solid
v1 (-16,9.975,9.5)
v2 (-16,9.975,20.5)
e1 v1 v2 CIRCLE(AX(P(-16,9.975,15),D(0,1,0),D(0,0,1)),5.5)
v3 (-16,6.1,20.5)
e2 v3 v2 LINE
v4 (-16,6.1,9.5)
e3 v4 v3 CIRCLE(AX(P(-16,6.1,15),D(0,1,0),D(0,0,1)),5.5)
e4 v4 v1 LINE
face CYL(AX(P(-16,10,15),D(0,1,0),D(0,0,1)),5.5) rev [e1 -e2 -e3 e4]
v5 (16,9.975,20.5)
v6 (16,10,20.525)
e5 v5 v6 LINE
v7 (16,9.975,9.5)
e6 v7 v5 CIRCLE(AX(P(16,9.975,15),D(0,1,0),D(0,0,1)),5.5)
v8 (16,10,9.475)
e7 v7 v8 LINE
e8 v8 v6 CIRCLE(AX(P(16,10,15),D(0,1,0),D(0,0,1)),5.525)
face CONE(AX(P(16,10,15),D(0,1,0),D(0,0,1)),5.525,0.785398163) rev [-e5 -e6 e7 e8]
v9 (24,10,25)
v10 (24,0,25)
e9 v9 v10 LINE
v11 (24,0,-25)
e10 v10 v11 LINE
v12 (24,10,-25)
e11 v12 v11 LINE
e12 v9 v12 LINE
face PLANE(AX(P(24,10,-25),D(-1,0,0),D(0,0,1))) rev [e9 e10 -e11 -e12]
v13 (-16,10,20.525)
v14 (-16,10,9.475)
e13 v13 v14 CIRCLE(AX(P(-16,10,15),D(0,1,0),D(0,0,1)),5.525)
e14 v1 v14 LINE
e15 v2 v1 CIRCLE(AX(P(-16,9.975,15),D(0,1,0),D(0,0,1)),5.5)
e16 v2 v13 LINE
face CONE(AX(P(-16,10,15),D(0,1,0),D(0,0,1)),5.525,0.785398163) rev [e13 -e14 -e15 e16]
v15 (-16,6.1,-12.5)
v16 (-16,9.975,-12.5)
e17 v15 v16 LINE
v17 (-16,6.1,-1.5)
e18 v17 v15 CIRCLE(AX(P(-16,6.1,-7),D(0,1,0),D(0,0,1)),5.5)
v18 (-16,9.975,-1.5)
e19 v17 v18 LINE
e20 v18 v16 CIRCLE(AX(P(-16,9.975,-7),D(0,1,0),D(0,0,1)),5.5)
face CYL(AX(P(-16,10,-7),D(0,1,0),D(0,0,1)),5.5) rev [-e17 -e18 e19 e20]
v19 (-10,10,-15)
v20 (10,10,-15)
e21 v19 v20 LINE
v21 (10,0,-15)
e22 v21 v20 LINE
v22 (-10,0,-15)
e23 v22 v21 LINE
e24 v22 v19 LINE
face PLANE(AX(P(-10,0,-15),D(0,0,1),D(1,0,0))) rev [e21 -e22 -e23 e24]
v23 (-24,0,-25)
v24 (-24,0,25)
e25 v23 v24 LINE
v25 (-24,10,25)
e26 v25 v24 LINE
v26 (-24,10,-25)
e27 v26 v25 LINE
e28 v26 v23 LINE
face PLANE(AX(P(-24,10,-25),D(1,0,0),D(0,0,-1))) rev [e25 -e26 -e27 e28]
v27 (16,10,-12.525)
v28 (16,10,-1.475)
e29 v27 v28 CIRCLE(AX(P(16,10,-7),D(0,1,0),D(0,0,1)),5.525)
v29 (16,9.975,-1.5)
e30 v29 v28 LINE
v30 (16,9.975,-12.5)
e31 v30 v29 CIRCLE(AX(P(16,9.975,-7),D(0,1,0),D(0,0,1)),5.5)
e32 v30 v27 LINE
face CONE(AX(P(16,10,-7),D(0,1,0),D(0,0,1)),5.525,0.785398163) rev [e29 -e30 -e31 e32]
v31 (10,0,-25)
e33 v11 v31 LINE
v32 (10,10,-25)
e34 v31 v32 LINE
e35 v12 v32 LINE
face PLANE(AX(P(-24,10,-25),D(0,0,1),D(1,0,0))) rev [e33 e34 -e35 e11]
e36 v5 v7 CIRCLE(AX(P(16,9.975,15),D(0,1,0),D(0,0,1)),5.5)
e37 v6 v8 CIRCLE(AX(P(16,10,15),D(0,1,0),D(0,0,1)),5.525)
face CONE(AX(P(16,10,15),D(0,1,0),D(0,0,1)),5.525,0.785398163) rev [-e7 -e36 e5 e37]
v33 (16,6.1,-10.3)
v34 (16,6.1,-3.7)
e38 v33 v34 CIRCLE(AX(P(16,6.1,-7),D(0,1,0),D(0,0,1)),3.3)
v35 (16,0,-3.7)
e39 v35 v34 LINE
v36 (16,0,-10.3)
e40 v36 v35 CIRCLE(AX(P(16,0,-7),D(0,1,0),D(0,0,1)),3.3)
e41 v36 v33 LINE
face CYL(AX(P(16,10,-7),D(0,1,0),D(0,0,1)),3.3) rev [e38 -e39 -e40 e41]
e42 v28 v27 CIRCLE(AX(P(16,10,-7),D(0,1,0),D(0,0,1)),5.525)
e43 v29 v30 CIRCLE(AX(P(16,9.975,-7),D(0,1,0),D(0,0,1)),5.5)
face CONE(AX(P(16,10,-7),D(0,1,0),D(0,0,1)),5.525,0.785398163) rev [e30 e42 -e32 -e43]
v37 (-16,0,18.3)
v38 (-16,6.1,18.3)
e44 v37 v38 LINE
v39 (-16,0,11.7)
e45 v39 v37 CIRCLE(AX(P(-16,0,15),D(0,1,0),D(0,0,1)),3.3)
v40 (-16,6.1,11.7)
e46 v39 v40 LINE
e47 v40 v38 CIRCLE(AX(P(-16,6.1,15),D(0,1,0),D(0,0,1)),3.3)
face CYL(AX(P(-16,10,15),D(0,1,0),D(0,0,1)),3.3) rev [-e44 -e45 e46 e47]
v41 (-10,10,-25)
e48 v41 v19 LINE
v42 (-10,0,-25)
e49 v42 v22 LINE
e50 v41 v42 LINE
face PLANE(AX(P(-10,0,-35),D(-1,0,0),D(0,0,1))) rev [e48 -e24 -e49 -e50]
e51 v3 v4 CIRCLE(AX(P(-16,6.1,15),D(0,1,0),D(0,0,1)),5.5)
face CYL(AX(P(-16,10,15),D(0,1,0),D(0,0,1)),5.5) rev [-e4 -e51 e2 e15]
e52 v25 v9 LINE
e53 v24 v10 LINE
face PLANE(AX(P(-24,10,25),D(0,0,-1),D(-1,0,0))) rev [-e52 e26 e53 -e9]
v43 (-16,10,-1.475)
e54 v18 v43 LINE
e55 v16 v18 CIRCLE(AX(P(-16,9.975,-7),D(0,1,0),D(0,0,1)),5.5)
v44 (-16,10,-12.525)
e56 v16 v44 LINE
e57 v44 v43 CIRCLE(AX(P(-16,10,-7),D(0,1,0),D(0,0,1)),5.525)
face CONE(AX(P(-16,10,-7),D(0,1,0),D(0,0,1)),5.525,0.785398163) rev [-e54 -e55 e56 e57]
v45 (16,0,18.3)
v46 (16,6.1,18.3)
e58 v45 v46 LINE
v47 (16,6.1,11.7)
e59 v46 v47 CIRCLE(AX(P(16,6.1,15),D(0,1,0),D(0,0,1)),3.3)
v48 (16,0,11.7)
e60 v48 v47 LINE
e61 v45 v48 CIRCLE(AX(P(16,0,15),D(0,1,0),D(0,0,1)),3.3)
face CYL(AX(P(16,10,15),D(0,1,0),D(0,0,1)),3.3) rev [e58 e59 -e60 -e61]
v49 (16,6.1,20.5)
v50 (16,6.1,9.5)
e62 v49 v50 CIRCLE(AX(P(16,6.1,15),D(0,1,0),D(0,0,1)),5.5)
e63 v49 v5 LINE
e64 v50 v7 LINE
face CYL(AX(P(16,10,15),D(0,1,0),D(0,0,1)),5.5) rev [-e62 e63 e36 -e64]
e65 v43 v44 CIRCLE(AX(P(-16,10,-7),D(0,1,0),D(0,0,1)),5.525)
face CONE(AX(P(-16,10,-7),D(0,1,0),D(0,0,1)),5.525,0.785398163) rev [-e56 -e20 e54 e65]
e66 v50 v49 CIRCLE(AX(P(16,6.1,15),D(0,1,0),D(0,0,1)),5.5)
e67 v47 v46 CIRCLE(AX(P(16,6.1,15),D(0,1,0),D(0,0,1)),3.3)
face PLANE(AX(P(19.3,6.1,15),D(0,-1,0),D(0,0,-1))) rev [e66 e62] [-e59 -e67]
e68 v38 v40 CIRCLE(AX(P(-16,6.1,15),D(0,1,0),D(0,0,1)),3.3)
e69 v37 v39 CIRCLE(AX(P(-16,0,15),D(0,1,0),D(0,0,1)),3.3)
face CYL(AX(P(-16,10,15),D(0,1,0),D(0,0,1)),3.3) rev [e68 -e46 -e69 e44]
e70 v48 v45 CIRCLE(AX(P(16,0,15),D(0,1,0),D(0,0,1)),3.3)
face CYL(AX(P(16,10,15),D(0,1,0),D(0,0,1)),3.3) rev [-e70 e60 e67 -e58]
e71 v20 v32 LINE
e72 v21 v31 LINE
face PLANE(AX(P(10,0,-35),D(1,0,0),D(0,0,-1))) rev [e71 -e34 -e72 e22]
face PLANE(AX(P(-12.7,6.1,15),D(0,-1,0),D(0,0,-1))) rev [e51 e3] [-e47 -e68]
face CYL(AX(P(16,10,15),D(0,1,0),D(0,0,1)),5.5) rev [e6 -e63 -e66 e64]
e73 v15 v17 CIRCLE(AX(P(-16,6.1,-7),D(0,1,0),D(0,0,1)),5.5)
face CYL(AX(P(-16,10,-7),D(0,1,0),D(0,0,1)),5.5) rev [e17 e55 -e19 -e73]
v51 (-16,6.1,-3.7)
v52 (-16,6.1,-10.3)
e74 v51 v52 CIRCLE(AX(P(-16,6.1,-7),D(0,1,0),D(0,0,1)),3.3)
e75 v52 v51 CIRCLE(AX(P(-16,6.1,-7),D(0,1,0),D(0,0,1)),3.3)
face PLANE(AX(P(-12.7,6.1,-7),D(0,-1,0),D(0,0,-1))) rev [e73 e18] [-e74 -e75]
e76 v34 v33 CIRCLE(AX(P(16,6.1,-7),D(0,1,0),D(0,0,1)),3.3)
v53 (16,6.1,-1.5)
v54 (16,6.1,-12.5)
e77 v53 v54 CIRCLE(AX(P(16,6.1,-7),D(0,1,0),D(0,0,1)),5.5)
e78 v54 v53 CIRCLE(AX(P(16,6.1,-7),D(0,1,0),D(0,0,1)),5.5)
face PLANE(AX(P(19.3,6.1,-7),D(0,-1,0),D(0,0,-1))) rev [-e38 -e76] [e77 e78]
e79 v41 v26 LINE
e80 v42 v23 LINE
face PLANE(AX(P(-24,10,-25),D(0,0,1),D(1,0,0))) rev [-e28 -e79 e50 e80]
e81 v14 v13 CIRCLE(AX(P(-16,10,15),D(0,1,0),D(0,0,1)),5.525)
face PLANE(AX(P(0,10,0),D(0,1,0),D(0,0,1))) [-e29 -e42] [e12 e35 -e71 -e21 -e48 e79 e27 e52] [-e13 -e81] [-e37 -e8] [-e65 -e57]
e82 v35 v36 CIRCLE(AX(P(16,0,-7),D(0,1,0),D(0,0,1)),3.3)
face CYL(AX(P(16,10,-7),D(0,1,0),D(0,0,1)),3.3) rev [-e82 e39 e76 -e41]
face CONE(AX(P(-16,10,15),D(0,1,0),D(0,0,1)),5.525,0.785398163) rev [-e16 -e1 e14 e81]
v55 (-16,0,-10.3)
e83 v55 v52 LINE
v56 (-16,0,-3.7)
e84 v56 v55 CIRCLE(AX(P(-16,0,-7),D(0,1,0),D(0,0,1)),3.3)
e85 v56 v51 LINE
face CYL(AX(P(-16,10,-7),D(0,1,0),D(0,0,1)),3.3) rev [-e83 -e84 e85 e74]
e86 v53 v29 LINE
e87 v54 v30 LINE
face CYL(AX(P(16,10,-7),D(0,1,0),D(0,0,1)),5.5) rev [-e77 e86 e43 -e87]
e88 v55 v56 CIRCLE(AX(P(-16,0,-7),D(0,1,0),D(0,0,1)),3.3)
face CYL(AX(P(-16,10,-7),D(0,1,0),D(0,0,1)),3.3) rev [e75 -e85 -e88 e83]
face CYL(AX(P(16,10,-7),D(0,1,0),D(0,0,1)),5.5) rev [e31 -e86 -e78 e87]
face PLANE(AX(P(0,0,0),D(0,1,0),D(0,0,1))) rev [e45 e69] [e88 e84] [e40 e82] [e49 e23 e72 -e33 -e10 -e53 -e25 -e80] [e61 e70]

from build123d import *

# Parameters (mm, degrees)
SKETCH1_W                                  = 48
SKETCH1_H                                  = 50
BOSS_EXTRUDE1_DEPTH                        = 10
SKETCH2_W                                  = 20
SKETCH2_H                                  = 20
CUT_EXTRUDE1_DEPTH                         = 10
CBORE_FOR_M6_CHEESE_HEAD_SCREW1_AT_2_COUNT = 2
CBORE_FOR_M6_CHEESE_HEAD_SCREW1_AT_2_PITCH = 22
CBORE_FOR_M6_CHEESE_HEAD_SCREW1_AT_3_COUNT = 2
CBORE_FOR_M6_CHEESE_HEAD_SCREW1_AT_3_PITCH = 38.832975678
CBORE_FOR_M6_CHEESE_HEAD_SCREW1_AT_4_COUNT = 2
CBORE_FOR_M6_CHEESE_HEAD_SCREW1_AT_4_PITCH = 32


with BuildPart() as part:
    # Sketch1 → Boss-Extrude1 (new body)
    with BuildSketch(Plane(origin=(0, 0, 0), x_dir=(1, 0, 0), z_dir=(0, 1, 0))):
        Rectangle(SKETCH1_W, SKETCH1_H)
    extrude(amount=BOSS_EXTRUDE1_DEPTH)

    # Sketch2 → Cut-Extrude1 (cut)
    with BuildSketch(Plane(origin=(0, 10, 0), x_dir=(1, 0, 0), z_dir=(0, 1, 0))):
        with Locations((0, 25)):
            Rectangle(SKETCH2_W, SKETCH2_H)
    extrude(amount=-CUT_EXTRUDE1_DEPTH, mode=Mode.SUBTRACT)

    # Sketch4 → CBORE for M6 Cheese Head Screw1 (revolve, cut)
    with BuildSketch(Plane(origin=(-16, 10, -7), x_dir=(0, 0, 1), z_dir=(1, 0, 0))):
        Polygon((0, 0), (0, 11.982840043), (3.3, 10), (3.3, 3.9), (5.5, 3.9), (5.5, 0.025), (5.525, 0), align=None)
    cbore_for_m6_cheese_head_screw1 = revolve(axis=Axis((-16, 16.35, -7), (0, -1, 0)), mode=Mode.SUBTRACT)

    # CBORE for M6 Cheese Head Screw1 at 2: CBORE for M6 Cheese Head Screw1 ×2
    with Locations(*[(0, 0, i * CBORE_FOR_M6_CHEESE_HEAD_SCREW1_AT_2_PITCH) for i in range(1, CBORE_FOR_M6_CHEESE_HEAD_SCREW1_AT_2_COUNT)]):
        add(cbore_for_m6_cheese_head_screw1, mode=Mode.SUBTRACT)

    # CBORE for M6 Cheese Head Screw1 at 3: CBORE for M6 Cheese Head Screw1 ×2
    with Locations(*[Vector(0.8240419241993677, 0, 0.5665288228870652) * (i * CBORE_FOR_M6_CHEESE_HEAD_SCREW1_AT_3_PITCH) for i in range(1, CBORE_FOR_M6_CHEESE_HEAD_SCREW1_AT_3_COUNT)]):
        add(cbore_for_m6_cheese_head_screw1, mode=Mode.SUBTRACT)

    # CBORE for M6 Cheese Head Screw1 at 4: CBORE for M6 Cheese Head Screw1 ×2
    with Locations(*[(i * CBORE_FOR_M6_CHEESE_HEAD_SCREW1_AT_4_PITCH, 0, 0) for i in range(1, CBORE_FOR_M6_CHEESE_HEAD_SCREW1_AT_4_COUNT)]):
        add(cbore_for_m6_cheese_head_screw1, mode=Mode.SUBTRACT)


solid = part.part
